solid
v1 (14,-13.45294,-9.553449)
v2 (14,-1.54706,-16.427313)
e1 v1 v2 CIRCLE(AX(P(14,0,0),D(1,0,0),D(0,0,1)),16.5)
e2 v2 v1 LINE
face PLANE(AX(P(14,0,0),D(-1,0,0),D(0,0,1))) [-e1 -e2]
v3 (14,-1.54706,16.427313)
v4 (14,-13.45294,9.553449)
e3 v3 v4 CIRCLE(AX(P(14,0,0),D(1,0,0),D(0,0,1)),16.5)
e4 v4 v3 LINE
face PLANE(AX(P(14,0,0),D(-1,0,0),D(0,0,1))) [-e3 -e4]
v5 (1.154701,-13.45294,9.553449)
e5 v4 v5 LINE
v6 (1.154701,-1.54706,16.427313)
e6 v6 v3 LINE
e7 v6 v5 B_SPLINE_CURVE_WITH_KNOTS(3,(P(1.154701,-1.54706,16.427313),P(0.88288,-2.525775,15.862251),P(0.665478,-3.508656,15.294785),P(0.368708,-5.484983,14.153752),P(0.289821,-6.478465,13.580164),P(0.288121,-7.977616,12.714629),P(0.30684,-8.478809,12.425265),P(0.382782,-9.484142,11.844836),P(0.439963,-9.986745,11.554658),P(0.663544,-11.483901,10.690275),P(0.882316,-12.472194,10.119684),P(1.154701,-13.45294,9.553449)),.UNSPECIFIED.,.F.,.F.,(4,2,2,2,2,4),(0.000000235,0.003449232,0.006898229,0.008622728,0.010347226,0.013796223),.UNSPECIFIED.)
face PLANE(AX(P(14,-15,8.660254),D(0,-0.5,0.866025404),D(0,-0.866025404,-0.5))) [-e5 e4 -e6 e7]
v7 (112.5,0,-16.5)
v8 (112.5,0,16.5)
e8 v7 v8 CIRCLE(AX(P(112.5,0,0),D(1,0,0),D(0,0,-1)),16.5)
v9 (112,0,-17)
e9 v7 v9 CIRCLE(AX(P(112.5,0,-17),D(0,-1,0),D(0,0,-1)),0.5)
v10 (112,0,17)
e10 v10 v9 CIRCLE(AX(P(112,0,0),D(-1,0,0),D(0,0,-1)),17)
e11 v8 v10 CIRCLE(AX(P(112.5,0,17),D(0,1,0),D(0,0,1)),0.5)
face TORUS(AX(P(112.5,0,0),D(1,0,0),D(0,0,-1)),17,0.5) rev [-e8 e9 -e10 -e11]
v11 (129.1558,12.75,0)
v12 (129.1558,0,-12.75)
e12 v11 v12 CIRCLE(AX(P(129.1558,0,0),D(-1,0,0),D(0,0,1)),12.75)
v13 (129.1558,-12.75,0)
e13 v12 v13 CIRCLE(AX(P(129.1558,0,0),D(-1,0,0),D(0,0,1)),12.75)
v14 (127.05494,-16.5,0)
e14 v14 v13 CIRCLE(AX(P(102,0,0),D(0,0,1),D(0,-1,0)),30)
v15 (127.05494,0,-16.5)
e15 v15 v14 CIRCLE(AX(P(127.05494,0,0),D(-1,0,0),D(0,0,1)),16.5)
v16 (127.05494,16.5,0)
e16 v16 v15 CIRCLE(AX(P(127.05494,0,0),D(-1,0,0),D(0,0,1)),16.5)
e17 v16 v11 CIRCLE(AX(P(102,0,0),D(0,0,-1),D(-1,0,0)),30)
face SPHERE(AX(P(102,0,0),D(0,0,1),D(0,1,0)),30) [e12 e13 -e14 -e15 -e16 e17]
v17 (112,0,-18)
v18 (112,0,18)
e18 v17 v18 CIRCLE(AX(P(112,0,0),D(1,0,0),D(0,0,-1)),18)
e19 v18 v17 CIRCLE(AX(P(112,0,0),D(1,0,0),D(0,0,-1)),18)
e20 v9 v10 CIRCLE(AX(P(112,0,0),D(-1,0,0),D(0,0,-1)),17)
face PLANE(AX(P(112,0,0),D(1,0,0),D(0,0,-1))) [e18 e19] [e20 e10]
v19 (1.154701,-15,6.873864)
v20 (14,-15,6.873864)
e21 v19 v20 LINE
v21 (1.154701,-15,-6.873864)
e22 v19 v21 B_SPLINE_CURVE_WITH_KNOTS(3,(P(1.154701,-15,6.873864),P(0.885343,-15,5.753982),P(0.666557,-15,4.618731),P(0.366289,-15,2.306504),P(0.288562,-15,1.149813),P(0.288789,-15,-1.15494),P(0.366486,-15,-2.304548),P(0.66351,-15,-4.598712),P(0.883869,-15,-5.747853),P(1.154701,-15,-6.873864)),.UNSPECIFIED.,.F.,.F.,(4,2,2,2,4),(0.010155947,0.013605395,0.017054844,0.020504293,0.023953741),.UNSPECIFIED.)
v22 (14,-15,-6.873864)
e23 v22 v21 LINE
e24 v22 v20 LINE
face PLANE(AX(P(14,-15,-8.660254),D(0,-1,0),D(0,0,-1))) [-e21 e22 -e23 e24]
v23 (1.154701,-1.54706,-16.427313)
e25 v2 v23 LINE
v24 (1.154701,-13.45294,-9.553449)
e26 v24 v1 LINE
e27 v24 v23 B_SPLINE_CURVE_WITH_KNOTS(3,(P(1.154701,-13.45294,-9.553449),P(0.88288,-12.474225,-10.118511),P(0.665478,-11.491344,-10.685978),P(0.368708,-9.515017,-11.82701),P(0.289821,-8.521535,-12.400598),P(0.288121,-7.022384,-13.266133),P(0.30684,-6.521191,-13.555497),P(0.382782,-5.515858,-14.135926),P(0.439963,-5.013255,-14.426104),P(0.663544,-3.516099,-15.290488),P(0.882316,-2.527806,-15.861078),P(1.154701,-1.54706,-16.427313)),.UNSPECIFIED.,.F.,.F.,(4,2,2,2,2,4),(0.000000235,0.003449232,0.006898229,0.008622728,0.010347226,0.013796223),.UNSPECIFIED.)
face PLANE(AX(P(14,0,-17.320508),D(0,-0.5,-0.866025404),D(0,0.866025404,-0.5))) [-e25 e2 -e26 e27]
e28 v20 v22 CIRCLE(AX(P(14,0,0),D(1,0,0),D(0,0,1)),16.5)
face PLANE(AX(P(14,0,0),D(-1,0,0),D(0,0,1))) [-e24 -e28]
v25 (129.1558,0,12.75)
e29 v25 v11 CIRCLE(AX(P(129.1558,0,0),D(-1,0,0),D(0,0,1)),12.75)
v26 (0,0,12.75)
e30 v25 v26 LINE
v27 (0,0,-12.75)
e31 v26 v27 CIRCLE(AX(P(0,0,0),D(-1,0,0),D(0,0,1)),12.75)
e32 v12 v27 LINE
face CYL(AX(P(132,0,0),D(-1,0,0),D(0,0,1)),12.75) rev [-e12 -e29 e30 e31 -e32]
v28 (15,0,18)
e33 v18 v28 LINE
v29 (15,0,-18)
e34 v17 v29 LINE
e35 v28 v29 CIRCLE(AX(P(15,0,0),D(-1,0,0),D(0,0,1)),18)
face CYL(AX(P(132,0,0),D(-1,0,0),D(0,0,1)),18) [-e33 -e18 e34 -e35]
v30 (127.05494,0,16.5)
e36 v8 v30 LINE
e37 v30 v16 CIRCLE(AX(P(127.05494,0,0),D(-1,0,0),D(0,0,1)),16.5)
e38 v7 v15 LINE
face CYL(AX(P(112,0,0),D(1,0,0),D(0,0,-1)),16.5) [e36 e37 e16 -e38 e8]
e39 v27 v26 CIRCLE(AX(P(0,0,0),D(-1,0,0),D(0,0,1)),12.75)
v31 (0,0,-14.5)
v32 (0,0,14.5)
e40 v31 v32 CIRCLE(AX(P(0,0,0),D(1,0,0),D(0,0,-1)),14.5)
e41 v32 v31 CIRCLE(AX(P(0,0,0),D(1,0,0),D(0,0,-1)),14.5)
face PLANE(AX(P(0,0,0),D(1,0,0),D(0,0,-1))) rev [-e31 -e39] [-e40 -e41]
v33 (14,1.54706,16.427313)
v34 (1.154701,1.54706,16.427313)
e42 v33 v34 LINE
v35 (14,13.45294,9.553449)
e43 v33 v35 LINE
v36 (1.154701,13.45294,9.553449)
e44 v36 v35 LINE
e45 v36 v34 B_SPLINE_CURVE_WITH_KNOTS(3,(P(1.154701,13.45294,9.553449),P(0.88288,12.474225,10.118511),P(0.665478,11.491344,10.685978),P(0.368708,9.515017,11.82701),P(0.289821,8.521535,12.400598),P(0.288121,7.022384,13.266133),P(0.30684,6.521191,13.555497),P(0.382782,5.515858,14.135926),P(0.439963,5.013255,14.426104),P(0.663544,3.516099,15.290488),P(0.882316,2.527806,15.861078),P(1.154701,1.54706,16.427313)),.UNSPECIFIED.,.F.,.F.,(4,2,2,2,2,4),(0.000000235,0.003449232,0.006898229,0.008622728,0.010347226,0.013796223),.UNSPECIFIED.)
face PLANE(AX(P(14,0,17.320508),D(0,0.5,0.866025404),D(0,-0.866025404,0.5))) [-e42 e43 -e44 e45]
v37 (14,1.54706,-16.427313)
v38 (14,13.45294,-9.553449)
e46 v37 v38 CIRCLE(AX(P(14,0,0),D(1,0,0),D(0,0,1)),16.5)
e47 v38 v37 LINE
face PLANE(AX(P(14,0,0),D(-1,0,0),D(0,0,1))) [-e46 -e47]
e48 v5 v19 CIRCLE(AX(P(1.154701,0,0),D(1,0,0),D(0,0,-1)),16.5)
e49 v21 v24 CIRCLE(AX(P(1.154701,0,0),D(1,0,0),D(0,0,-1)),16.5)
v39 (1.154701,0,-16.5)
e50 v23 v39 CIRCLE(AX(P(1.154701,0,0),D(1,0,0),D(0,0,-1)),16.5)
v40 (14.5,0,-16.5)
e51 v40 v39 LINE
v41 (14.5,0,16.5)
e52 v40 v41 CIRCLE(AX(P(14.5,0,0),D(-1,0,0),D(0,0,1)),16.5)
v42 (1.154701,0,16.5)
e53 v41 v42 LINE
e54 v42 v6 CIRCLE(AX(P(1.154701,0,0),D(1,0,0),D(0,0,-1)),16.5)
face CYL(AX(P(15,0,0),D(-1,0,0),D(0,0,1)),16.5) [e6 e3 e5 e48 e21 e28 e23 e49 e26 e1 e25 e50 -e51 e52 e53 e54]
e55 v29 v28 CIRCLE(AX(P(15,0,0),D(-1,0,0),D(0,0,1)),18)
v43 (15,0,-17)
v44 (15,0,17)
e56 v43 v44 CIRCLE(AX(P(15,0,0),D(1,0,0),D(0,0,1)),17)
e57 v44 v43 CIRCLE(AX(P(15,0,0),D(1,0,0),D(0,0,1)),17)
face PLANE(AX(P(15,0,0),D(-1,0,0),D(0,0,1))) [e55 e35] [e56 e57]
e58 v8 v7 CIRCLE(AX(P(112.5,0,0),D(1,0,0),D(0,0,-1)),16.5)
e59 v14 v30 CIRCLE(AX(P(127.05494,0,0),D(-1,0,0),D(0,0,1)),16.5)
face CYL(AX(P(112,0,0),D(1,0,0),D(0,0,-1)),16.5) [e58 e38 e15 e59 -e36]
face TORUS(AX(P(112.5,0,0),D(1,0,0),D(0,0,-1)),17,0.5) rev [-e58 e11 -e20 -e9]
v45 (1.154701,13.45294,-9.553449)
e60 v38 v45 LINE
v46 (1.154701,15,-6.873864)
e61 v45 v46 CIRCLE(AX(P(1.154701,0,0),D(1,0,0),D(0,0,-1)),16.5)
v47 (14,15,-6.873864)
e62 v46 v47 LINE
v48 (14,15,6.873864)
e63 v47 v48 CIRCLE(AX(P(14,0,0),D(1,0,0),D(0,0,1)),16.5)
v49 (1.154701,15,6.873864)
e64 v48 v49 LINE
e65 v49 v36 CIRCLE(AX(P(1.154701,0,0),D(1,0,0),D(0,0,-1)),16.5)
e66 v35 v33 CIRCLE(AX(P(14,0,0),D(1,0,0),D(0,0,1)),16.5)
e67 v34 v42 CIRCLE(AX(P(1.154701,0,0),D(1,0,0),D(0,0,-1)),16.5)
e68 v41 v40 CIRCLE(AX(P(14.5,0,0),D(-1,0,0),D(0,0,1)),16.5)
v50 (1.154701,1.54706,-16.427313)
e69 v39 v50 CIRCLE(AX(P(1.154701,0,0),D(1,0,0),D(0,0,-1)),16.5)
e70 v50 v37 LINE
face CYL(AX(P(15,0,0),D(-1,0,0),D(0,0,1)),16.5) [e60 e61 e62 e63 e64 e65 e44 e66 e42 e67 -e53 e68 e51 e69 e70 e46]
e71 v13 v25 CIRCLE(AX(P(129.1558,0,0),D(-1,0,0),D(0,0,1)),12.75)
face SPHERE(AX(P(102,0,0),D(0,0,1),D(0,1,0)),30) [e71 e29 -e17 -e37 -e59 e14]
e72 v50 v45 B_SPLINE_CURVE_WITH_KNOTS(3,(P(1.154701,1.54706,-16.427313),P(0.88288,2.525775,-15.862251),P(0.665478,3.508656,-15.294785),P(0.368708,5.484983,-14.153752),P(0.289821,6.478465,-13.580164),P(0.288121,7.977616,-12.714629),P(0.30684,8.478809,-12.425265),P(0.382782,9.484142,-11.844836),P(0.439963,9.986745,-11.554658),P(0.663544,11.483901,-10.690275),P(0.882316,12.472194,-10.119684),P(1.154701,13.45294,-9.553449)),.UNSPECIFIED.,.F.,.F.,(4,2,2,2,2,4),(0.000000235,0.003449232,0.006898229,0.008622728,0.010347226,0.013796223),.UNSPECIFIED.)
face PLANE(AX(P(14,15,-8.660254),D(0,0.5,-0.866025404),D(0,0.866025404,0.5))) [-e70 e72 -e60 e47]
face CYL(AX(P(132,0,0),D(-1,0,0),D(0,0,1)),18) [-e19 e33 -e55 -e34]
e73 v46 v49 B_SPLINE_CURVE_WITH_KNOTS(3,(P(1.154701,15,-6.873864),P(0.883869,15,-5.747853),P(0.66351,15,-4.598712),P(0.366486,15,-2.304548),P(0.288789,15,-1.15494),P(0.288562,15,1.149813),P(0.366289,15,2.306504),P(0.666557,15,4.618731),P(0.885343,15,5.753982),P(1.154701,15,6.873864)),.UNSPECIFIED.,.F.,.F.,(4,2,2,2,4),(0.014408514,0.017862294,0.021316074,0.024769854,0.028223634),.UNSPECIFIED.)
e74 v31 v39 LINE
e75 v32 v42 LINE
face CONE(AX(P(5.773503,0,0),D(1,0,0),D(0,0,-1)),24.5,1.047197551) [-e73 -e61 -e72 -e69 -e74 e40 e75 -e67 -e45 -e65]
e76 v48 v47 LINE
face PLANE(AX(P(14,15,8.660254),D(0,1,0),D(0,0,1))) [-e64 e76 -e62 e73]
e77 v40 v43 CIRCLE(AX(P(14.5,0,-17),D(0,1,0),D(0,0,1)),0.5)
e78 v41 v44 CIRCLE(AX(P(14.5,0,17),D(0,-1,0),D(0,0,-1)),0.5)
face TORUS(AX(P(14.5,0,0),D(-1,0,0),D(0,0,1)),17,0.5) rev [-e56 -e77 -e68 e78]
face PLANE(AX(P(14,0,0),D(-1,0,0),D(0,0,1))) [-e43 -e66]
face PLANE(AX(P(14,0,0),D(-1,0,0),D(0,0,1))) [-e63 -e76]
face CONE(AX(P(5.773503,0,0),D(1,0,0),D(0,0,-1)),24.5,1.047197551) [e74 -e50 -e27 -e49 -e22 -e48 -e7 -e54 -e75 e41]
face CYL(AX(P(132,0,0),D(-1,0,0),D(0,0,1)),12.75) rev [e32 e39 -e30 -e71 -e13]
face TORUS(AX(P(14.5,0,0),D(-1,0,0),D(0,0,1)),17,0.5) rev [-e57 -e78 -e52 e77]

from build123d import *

# Parameters (mm, degrees)
SKETCH1_R          = 18
EXTRUDE1_DEPTH     = 132
SKETCH2_R          = 12.75
CUT_EXTRUDE1_DEPTH = 135.432139014
SKETCH3_R          = 18
SKETCH3_R_2        = 16.5
CUT_EXTRUDE2_DEPTH = 15
CUT_EXTRUDE3_START = -20
SKETCH4_R          = 18
SKETCH4_R_2        = 16.5
CUT_EXTRUDE3_DEPTH = 20
FILLET1_R          = 0.5
SKETCH6_R          = 25
CUT_EXTRUDE4_DEPTH = 14


with BuildPart() as part:
    # Sketch1 → Extrude1 (new body)
    with BuildSketch(Plane(origin=(0, 0, 0), x_dir=(0, 0, -1), z_dir=(1, 0, 0))):
        Circle(SKETCH1_R)
    extrude(amount=EXTRUDE1_DEPTH)

    # Sketch2 → Cut-Extrude1 (cut, through all)
    with BuildSketch(Plane.ZY):
        Circle(SKETCH2_R)
    extrude(amount=-CUT_EXTRUDE1_DEPTH, mode=Mode.SUBTRACT)

    # Sketch3 → Cut-Extrude2 (cut)
    with BuildSketch(Plane.ZY):
        Circle(SKETCH3_R)
        Circle(SKETCH3_R_2, mode=Mode.SUBTRACT)
    extrude(amount=-CUT_EXTRUDE2_DEPTH, mode=Mode.SUBTRACT)

    # Sketch4 → Cut-Extrude3 (cut)
    with BuildSketch(Plane(origin=(132, 0, 0), x_dir=(0, 0, -1), z_dir=(1, 0, 0)).offset(CUT_EXTRUDE3_START)):
        with Locations(Location((0, 0, 0), (0, 0, 180))):
            Circle(SKETCH4_R)
        with Locations(Location((0, 0, 0), (0, 0, 180))):
            Circle(SKETCH4_R_2, mode=Mode.SUBTRACT)
    extrude(amount=CUT_EXTRUDE3_DEPTH, mode=Mode.SUBTRACT)

    # Fillet1
    fillet1_edges = [part.edges().sort_by_distance(p)[0] for p in [
        (15, 0, -16.5),
        (112, 0, -16.5),
    ]]
    fillet(fillet1_edges, radius=FILLET1_R)

    # Sketch5 → Cut-Revolve1 (revolve, cut)
    with BuildSketch(Plane.XY, mode=Mode.PRIVATE) as cut_revolve1_sk:
        with BuildLine():
            Line((119.041447752, -42.253356684), (137.021599533, -42.253356684))
            Line((137.021599533, -42.253356684), (137.021599533, 0))
            Line((137.021599533, 0), (132, 0))
            ThreePointArc((132, 0), (128.56354111, -13.941961258), (119.041447752, -24.689857401))
            Line((119.041447752, -24.689857401), (119.041447752, -42.253356684))
        make_face()
    revolve(cut_revolve1_sk.sketch.rotate(Axis((132, 0, 0), (-1, 0, 0)), 180), axis=Axis((132, 0, 0), (-1, 0, 0)), mode=Mode.SUBTRACT)

    # Sketch6 → Cut-Extrude4 (cut)
    with BuildSketch(Plane.ZY):
        Circle(SKETCH6_R)
        Polygon((-8.660254038, -15), (8.660254038, -15), (17.320508076, 0), (8.660254038, 15), (-8.660254038, 15), (-17.320508076, 0), align=None, mode=Mode.SUBTRACT)
    extrude(amount=-CUT_EXTRUDE4_DEPTH, mode=Mode.SUBTRACT)

    # Sketch7 → Cut-Revolve2 (revolve, cut)
    with BuildSketch(Plane.XY, mode=Mode.PRIVATE) as cut_revolve2_sk:
        Polygon((0, -14.5), (0, -24.5), (5.773502692, -24.5), align=None)
    revolve(cut_revolve2_sk.sketch.rotate(Axis((15, 0, 0), (-1, 0, 0)), 270), axis=Axis((15, 0, 0), (-1, 0, 0)), mode=Mode.SUBTRACT)


solid = part.part
